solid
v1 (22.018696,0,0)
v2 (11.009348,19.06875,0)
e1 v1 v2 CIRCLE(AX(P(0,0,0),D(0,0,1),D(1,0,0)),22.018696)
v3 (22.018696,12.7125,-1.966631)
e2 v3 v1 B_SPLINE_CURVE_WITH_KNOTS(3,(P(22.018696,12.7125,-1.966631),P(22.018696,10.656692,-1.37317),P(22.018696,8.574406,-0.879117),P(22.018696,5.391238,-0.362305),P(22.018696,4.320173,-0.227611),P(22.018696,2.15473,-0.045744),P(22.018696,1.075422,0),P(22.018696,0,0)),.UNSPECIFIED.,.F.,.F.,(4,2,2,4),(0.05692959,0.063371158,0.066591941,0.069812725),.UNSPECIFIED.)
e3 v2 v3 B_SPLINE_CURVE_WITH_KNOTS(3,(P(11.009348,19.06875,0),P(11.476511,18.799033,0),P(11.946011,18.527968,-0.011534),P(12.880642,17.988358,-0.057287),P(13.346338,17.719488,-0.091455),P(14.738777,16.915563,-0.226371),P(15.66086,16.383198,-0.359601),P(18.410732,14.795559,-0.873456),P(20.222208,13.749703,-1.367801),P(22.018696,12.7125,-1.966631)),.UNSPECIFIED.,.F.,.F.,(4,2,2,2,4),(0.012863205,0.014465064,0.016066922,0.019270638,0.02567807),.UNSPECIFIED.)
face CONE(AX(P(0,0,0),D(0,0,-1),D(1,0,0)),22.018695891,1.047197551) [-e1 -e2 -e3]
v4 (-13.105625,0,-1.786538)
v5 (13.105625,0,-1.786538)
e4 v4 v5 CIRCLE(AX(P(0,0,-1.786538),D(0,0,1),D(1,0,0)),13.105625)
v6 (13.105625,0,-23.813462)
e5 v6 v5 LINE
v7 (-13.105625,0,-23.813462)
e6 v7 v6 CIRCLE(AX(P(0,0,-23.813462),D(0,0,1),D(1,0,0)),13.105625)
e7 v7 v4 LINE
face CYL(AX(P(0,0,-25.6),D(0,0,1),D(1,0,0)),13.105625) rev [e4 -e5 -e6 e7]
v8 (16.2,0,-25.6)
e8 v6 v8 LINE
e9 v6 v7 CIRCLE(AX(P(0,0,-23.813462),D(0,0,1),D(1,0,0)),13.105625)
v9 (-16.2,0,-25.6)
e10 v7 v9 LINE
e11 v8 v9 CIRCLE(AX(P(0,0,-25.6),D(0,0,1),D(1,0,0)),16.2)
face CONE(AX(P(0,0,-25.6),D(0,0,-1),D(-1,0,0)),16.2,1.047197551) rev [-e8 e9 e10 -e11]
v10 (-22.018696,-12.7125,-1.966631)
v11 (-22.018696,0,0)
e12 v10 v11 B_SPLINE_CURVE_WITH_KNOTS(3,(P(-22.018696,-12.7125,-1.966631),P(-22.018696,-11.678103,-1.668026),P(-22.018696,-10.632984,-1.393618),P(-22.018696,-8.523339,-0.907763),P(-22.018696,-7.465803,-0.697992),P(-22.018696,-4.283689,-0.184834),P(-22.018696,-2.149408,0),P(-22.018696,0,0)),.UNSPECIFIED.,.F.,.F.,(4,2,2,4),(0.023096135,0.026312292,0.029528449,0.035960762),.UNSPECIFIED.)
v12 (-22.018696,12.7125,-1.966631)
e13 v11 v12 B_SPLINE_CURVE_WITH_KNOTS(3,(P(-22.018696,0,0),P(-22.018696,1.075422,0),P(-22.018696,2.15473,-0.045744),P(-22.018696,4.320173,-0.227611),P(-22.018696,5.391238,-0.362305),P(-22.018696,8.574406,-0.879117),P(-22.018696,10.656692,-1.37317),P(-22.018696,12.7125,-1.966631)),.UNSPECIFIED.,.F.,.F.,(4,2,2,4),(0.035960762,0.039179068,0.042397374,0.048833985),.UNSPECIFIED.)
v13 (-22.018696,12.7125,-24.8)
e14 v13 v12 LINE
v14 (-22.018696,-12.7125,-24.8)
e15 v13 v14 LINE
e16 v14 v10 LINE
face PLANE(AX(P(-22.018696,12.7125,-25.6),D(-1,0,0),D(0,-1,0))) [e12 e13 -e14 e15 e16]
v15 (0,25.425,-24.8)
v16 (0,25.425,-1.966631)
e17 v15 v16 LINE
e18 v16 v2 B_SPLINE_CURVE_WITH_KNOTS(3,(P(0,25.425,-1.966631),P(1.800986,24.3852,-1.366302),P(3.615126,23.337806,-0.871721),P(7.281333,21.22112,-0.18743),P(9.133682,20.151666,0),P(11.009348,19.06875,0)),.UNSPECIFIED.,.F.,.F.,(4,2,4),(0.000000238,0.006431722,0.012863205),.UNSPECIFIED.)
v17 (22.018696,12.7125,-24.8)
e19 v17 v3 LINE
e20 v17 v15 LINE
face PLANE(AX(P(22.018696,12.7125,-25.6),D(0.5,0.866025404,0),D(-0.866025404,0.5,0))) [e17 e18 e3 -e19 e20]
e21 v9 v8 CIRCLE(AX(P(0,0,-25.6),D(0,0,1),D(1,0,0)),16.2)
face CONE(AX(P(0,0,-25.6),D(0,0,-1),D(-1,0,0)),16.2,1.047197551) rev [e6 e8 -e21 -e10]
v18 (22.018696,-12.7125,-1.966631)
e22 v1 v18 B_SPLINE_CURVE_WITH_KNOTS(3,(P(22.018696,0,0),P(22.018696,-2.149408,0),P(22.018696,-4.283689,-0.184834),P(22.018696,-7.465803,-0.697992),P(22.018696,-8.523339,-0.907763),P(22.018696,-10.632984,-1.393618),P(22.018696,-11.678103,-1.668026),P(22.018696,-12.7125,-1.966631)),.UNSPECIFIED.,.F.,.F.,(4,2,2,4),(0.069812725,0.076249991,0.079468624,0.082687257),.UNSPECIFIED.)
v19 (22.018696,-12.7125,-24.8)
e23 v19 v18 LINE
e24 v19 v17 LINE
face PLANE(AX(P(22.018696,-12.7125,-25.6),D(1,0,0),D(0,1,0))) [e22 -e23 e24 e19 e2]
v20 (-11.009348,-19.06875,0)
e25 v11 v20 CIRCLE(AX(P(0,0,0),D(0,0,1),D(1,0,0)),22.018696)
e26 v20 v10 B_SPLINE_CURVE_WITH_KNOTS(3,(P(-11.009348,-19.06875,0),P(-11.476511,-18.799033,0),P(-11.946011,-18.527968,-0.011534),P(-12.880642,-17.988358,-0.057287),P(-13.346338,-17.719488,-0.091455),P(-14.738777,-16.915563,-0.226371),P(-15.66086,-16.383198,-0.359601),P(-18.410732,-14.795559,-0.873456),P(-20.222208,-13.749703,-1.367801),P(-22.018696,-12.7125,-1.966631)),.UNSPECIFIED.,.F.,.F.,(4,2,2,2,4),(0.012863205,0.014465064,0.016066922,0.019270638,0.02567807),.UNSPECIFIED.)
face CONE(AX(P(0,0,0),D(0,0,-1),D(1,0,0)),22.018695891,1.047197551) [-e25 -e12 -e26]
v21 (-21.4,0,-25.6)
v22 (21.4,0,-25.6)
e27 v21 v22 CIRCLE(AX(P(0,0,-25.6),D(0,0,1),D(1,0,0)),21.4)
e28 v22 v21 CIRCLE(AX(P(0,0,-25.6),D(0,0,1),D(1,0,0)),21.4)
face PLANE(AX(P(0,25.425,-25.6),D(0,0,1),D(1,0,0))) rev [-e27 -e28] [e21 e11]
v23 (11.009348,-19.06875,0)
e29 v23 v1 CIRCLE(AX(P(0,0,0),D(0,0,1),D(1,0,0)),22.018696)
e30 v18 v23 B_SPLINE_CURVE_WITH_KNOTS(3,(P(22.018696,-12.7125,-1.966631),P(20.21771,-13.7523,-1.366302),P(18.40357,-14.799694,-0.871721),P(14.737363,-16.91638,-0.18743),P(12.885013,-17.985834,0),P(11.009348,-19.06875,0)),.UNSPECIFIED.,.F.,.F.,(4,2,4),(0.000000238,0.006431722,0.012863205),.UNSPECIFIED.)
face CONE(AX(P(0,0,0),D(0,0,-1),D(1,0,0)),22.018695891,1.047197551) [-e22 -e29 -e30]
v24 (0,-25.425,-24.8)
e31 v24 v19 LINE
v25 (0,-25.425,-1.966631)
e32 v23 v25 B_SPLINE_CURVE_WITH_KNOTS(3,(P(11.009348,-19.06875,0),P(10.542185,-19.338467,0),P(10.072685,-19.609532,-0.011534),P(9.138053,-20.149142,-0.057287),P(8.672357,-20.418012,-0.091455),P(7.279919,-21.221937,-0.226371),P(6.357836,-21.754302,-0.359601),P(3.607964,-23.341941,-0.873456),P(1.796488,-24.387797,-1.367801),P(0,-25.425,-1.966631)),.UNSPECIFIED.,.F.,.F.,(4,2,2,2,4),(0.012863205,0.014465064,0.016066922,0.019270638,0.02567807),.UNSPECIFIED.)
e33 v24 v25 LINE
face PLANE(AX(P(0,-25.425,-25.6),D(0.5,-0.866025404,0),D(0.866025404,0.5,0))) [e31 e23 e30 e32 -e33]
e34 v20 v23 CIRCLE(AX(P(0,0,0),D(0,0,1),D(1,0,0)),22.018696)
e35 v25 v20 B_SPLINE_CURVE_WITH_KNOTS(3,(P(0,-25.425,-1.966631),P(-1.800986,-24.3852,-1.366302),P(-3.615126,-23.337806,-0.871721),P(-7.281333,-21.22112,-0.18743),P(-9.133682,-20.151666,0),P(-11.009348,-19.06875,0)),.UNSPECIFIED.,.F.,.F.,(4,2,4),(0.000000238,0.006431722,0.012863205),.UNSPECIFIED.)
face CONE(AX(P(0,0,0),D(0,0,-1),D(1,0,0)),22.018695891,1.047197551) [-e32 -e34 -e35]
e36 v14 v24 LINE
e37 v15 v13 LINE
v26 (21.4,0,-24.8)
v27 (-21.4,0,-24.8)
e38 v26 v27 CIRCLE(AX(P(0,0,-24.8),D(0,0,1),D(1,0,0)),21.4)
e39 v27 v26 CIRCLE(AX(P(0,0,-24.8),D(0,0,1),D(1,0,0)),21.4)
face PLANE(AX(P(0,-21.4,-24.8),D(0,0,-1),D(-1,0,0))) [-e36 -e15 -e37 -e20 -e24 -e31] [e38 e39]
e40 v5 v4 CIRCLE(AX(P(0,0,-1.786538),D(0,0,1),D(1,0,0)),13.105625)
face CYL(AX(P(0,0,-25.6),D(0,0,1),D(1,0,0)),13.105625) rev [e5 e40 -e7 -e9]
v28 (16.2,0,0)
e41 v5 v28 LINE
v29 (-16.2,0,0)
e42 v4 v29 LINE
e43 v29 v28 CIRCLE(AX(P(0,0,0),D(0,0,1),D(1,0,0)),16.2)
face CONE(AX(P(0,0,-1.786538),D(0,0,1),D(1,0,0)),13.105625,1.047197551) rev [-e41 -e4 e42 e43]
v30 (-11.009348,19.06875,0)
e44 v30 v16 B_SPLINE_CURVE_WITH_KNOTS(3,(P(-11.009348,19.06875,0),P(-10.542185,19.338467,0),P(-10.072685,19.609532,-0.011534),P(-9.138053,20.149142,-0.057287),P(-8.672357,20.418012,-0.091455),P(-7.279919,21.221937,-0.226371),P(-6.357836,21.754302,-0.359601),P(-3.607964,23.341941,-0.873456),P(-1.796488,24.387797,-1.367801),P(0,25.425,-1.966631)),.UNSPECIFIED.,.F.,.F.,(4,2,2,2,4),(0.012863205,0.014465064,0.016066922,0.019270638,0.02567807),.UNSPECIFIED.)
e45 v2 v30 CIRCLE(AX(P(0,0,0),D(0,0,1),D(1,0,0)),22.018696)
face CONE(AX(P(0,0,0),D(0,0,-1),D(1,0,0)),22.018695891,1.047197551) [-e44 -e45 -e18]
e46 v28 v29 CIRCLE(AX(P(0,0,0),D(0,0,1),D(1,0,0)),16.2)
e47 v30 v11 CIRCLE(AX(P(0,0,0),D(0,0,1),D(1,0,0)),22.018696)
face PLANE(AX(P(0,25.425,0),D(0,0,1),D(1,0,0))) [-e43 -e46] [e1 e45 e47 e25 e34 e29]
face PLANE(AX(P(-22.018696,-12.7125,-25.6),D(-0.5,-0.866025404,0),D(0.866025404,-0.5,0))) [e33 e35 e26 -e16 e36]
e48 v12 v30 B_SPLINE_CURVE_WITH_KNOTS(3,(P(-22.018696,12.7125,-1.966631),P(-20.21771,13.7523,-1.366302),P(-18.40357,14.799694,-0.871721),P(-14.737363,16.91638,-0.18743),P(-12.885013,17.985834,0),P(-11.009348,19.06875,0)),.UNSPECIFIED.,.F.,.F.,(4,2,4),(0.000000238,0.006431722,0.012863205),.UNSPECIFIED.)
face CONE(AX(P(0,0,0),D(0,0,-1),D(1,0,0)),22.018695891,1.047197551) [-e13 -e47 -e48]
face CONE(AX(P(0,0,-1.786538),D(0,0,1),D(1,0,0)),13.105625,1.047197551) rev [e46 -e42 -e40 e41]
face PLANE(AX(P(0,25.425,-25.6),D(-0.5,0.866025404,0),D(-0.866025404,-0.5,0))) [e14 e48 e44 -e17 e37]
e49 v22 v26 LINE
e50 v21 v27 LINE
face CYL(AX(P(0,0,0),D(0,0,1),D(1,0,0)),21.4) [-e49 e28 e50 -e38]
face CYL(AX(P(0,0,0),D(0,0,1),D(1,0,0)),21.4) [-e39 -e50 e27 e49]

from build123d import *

# Parameters (mm, degrees)
SKETCH_3_R          = 13.105625
EXTRUDE_1_DEPTH     = 25.6
SKETCH_5_R          = 38.1375
SKETCH_5_R_2        = 22.018695891
CUT_EXTRUDE_1_DEPTH = 5.12
CUT_EXTRUDE_1_DRAFT = -60
SKETCH_6_W          = 0.8
SKETCH_6_H          = 4.025


with BuildPart() as part:
    # 草图3 → 凸台-拉伸1 (new body)
    with BuildSketch(Plane.XY):
        Polygon((0, 25.425), (-22.018695891, 12.7125), (-22.018695891, -12.7125), (0, -25.425), (22.018695891, -12.7125), (22.018695891, 12.7125), align=None)
        Circle(SKETCH_3_R, mode=Mode.SUBTRACT)
    extrude(amount=-EXTRUDE_1_DEPTH)

    # 草图4 → 切除-旋转1 (revolve, cut)
    with BuildSketch(Plane(origin=(0, 0, 0), x_dir=(0, 0, -1), z_dir=(1, 0, 0)), mode=Mode.PRIVATE) as cut_revolve_1_sk:
        Polygon((0, 16.2), (1.786538239, 13.105625), (1.786538239, 0), (0, 0), align=None)
        Polygon((25.6, 0), (25.6, 16.2), (23.813461761, 13.105625), (23.813461761, 0), align=None)
    revolve(cut_revolve_1_sk.sketch.rotate(Axis((0, 0, 0), (0, 0, -1)), 90), axis=Axis((0, 0, 0), (0, 0, -1)), mode=Mode.SUBTRACT)


with BuildPart() as cut_extrude_1_tool:
    # 草图5 → 切除-拉伸1 (with draft: the straight prism first)
    with BuildSketch(Plane.XY):
        Circle(SKETCH_5_R)
        Circle(SKETCH_5_R_2, mode=Mode.SUBTRACT)
    extrude(amount=-CUT_EXTRUDE_1_DEPTH)
    # 切除-拉伸1: the draft: its side faces are tilted about the plane it starts from
    cut_extrude_1_sides = [cut_extrude_1_tool.faces().sort_by_distance(p)[0] for p in [
        (-38.1375, 0, -2.56),
        (-22.018695891, 0, -2.56),
    ]]
    draft(cut_extrude_1_sides, Plane.XY, CUT_EXTRUDE_1_DRAFT)


with BuildPart() as part_1:
    add(part.part)

    # 切除-拉伸1: cut by cut_extrude_1_tool
    add(cut_extrude_1_tool.part, mode=Mode.SUBTRACT)

    # 草图6 → 切除-旋转2 (revolve, cut)
    with BuildSketch(Plane(origin=(0, 0, 0), x_dir=(0, 0, -1), z_dir=(1, 0, 0)), mode=Mode.PRIVATE) as cut_revolve_2_sk:
        with Locations((25.2, 23.4125)):
            Rectangle(SKETCH_6_W, SKETCH_6_H)
    revolve(cut_revolve_2_sk.sketch.rotate(Axis((0, 0, 0), (0, 0, -1)), 90), axis=Axis((0, 0, 0), (0, 0, -1)), mode=Mode.SUBTRACT)


solid = part_1.part
